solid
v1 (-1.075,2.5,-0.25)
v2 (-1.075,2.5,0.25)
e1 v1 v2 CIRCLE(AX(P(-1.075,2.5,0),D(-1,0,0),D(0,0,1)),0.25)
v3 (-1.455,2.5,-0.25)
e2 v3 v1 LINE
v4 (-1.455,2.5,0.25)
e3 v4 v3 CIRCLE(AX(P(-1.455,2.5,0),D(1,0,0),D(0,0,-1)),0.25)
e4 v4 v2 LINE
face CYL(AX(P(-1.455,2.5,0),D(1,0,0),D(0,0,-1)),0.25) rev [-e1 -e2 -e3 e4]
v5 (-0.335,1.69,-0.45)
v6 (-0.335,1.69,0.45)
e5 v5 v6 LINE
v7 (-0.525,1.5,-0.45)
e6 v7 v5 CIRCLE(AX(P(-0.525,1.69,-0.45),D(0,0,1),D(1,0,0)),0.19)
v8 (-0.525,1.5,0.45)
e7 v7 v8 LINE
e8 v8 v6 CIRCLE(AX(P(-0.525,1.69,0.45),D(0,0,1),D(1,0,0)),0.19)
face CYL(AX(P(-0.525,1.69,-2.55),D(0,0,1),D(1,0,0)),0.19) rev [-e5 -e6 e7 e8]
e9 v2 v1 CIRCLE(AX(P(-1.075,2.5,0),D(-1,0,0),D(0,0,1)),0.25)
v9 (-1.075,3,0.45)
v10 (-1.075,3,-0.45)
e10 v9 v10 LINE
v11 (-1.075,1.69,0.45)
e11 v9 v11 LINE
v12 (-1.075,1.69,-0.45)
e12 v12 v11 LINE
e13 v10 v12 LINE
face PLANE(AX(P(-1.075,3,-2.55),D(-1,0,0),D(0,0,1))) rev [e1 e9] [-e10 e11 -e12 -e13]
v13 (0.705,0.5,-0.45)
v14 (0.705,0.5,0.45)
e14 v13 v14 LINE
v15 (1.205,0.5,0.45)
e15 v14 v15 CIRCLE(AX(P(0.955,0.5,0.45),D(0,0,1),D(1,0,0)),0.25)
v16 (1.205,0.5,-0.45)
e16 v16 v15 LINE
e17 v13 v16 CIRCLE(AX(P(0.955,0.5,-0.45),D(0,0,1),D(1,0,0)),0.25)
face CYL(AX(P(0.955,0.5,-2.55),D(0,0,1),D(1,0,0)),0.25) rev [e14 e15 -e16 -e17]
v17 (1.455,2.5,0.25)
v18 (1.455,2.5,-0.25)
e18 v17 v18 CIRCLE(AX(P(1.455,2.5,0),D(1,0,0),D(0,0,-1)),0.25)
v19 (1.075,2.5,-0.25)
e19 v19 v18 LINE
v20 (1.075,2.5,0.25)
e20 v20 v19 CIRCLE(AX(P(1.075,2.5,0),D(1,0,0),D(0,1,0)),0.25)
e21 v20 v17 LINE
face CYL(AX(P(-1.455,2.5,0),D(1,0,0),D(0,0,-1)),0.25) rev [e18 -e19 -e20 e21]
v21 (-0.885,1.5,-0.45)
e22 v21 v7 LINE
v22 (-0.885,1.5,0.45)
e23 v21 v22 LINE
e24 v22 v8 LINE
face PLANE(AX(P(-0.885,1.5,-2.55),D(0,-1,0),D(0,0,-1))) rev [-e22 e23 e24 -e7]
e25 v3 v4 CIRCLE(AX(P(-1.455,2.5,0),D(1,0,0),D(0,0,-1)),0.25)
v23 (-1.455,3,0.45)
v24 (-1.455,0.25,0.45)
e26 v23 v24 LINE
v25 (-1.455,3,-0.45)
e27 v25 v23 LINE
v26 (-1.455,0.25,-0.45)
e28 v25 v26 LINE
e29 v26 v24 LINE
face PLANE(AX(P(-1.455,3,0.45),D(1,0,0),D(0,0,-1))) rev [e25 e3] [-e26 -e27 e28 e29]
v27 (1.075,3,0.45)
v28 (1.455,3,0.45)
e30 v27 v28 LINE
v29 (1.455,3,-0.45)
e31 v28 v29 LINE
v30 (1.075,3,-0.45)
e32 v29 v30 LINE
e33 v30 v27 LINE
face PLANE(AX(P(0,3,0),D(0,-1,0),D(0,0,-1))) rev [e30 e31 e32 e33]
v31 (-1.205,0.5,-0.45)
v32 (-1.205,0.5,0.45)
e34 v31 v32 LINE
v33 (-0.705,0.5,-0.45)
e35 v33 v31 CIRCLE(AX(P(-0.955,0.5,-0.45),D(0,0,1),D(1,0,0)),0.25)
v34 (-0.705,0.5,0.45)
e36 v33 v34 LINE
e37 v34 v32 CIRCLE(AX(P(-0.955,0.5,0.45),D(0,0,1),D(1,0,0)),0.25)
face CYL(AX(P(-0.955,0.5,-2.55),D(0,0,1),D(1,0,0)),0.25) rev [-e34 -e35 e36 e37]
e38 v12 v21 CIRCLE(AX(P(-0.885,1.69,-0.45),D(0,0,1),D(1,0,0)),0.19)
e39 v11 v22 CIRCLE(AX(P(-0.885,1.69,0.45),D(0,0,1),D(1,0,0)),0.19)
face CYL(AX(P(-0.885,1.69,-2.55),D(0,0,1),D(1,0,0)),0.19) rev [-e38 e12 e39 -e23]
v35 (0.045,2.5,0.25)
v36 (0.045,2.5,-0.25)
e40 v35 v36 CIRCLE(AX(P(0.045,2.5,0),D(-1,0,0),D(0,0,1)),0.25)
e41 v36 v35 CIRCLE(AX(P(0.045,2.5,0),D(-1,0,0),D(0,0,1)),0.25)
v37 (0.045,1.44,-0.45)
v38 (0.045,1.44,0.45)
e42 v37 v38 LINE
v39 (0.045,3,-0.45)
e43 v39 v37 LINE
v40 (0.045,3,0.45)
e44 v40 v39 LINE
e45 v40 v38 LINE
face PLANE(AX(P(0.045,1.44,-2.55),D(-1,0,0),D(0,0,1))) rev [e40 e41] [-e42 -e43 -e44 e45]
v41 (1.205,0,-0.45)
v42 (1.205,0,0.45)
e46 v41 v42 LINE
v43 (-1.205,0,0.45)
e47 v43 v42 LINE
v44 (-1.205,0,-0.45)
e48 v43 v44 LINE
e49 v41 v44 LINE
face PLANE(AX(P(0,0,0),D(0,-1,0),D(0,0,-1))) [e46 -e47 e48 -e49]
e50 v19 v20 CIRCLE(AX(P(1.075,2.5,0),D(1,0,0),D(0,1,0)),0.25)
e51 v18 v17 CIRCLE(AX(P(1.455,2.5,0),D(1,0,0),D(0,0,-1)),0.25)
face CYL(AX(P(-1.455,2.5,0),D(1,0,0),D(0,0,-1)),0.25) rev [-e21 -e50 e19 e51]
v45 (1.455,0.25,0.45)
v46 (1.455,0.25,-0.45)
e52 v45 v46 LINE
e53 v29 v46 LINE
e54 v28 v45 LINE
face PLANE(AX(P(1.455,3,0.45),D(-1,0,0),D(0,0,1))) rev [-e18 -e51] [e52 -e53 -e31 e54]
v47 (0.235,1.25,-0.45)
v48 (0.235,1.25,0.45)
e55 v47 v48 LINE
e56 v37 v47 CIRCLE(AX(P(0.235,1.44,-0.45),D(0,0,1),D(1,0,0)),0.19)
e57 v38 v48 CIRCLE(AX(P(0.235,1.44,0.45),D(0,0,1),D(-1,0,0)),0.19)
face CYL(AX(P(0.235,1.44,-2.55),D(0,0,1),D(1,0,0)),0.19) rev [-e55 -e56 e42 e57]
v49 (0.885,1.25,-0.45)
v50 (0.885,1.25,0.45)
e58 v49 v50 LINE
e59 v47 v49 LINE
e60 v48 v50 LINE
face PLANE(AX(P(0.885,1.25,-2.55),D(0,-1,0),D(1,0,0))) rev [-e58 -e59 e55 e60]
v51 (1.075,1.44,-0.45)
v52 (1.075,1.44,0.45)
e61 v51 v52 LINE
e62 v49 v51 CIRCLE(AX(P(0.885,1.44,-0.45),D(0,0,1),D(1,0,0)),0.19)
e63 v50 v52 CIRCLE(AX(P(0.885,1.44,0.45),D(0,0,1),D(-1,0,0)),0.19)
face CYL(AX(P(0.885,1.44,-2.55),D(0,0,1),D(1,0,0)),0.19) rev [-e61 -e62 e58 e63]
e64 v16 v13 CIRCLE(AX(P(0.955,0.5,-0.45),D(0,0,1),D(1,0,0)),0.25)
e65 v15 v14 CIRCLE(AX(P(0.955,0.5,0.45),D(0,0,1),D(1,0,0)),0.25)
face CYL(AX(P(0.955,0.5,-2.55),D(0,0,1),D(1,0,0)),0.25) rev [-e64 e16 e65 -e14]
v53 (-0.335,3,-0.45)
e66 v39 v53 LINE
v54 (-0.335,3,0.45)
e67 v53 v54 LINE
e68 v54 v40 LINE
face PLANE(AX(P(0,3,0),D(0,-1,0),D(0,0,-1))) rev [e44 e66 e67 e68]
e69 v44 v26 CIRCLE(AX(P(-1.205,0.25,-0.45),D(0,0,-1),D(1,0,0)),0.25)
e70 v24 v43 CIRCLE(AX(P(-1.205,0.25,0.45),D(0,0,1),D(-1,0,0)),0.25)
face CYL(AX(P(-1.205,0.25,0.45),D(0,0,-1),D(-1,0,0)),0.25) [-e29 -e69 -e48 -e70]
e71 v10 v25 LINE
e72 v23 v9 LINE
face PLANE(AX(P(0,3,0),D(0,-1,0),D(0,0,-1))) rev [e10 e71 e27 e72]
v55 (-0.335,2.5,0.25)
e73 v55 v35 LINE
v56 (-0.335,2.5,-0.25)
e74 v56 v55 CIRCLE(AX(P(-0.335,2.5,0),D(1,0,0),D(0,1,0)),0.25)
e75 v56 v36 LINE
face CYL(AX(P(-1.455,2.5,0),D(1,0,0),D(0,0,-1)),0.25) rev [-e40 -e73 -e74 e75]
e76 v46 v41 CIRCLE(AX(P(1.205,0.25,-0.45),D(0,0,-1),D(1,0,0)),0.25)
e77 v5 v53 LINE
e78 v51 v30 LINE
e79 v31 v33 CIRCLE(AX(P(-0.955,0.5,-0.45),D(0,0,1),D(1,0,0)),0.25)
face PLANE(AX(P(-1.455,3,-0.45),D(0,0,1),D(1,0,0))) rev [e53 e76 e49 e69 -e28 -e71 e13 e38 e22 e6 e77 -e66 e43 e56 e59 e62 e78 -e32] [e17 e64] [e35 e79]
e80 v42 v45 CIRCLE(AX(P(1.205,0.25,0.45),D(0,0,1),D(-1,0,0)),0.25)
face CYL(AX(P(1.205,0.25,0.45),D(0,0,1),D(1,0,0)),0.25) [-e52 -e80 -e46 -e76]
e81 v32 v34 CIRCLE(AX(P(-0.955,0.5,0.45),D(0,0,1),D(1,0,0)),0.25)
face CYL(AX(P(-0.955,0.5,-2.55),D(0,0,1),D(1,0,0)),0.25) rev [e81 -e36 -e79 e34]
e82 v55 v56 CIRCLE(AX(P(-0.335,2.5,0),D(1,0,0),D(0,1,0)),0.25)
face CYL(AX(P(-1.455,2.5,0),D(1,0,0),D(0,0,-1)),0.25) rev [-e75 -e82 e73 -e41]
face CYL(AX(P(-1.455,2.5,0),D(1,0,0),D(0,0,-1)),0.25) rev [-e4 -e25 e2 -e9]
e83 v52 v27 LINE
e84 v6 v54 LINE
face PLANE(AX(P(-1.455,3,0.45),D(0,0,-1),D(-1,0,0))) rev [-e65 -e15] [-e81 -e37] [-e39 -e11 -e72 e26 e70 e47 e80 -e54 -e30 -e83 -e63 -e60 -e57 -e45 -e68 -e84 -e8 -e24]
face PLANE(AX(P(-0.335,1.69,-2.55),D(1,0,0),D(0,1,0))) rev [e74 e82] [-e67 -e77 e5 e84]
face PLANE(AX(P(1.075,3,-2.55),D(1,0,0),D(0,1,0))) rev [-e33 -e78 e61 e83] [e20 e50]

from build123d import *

# Parameters (mm, degrees)
BRACKET_PLATE_PROFILE_W = 2.91
BRACKET_PLATE_PROFILE_H = 0.9
BRACKET_PLATE_DEPTH     = 3
CORNER_FILLET_R0_25_R   = 0.25
PRONG_SLOTS_DEPTH       = 3
MOUNTING_HOLES_SKETCH_R = 0.25
MOUNTING_HOLES_2X_DEPTH = 3
CROSS_PIN_BORE_SKETCH_R = 0.25
CROSS_PIN_BORE_DEPTH    = 5.203641279


with BuildPart() as part:
    # Bracket Plate Profile → Bracket Plate (new body)
    with BuildSketch(Plane(origin=(0, 0, 0), x_dir=(1, 0, 0), z_dir=(0, 1, 0))):
        Rectangle(BRACKET_PLATE_PROFILE_W, BRACKET_PLATE_PROFILE_H)
    extrude(amount=BRACKET_PLATE_DEPTH)

    # Corner Fillet R0.25
    corner_fillet_r0_25_edges = [part.edges().sort_by_distance(p)[0] for p in [
        (-1.455, 0, 0),
        (1.455, 0, 0),
    ]]
    fillet(corner_fillet_r0_25_edges, radius=CORNER_FILLET_R0_25_R)

    # Prong Slots Sketch → Prong Slots (cut)
    with BuildSketch(Plane.XY.offset(0.45)):
        with BuildLine():
            Line((-1.075, 3), (-1.075, 1.69))
            ThreePointArc((-1.075, 1.69), (-1.019350288, 1.555649712), (-0.885, 1.5))
            Line((-0.885, 1.5), (-0.525, 1.5))
            ThreePointArc((-0.525, 1.5), (-0.390649712, 1.555649712), (-0.335, 1.69))
            Line((-0.335, 1.69), (-0.335, 3))
            Line((-0.335, 3), (-1.075, 3))
        make_face()
        with BuildLine():
            Line((1.075, 3), (1.075, 1.44))
            ThreePointArc((1.075, 1.44), (1.019350288, 1.305649712), (0.885, 1.25))
            Line((0.885, 1.25), (0.235, 1.25))
            ThreePointArc((0.235, 1.25), (0.100649712, 1.305649712), (0.045, 1.44))
            Line((0.045, 1.44), (0.045, 3))
            Line((0.045, 3), (1.075, 3))
        make_face()
    extrude(amount=-PRONG_SLOTS_DEPTH, mode=Mode.SUBTRACT)

    # Mounting Holes Sketch → Mounting Holes 2x (cut)
    with BuildSketch(Plane.XY.offset(0.45)):
        with Locations((-0.955, 0.5)):
            Circle(MOUNTING_HOLES_SKETCH_R)
        with Locations((0.955, 0.5)):
            Circle(MOUNTING_HOLES_SKETCH_R)
    extrude(amount=-MOUNTING_HOLES_2X_DEPTH, mode=Mode.SUBTRACT)

    # Cross Pin Bore Sketch → Cross Pin Bore (cut, through all)
    with BuildSketch(Plane(origin=(1.455, 0, 0), x_dir=(0, 0, -1), z_dir=(1, 0, 0))):
        with Locations((0, 2.5)):
            Circle(CROSS_PIN_BORE_SKETCH_R)
    extrude(amount=-CROSS_PIN_BORE_DEPTH, mode=Mode.SUBTRACT)


solid = part.part
